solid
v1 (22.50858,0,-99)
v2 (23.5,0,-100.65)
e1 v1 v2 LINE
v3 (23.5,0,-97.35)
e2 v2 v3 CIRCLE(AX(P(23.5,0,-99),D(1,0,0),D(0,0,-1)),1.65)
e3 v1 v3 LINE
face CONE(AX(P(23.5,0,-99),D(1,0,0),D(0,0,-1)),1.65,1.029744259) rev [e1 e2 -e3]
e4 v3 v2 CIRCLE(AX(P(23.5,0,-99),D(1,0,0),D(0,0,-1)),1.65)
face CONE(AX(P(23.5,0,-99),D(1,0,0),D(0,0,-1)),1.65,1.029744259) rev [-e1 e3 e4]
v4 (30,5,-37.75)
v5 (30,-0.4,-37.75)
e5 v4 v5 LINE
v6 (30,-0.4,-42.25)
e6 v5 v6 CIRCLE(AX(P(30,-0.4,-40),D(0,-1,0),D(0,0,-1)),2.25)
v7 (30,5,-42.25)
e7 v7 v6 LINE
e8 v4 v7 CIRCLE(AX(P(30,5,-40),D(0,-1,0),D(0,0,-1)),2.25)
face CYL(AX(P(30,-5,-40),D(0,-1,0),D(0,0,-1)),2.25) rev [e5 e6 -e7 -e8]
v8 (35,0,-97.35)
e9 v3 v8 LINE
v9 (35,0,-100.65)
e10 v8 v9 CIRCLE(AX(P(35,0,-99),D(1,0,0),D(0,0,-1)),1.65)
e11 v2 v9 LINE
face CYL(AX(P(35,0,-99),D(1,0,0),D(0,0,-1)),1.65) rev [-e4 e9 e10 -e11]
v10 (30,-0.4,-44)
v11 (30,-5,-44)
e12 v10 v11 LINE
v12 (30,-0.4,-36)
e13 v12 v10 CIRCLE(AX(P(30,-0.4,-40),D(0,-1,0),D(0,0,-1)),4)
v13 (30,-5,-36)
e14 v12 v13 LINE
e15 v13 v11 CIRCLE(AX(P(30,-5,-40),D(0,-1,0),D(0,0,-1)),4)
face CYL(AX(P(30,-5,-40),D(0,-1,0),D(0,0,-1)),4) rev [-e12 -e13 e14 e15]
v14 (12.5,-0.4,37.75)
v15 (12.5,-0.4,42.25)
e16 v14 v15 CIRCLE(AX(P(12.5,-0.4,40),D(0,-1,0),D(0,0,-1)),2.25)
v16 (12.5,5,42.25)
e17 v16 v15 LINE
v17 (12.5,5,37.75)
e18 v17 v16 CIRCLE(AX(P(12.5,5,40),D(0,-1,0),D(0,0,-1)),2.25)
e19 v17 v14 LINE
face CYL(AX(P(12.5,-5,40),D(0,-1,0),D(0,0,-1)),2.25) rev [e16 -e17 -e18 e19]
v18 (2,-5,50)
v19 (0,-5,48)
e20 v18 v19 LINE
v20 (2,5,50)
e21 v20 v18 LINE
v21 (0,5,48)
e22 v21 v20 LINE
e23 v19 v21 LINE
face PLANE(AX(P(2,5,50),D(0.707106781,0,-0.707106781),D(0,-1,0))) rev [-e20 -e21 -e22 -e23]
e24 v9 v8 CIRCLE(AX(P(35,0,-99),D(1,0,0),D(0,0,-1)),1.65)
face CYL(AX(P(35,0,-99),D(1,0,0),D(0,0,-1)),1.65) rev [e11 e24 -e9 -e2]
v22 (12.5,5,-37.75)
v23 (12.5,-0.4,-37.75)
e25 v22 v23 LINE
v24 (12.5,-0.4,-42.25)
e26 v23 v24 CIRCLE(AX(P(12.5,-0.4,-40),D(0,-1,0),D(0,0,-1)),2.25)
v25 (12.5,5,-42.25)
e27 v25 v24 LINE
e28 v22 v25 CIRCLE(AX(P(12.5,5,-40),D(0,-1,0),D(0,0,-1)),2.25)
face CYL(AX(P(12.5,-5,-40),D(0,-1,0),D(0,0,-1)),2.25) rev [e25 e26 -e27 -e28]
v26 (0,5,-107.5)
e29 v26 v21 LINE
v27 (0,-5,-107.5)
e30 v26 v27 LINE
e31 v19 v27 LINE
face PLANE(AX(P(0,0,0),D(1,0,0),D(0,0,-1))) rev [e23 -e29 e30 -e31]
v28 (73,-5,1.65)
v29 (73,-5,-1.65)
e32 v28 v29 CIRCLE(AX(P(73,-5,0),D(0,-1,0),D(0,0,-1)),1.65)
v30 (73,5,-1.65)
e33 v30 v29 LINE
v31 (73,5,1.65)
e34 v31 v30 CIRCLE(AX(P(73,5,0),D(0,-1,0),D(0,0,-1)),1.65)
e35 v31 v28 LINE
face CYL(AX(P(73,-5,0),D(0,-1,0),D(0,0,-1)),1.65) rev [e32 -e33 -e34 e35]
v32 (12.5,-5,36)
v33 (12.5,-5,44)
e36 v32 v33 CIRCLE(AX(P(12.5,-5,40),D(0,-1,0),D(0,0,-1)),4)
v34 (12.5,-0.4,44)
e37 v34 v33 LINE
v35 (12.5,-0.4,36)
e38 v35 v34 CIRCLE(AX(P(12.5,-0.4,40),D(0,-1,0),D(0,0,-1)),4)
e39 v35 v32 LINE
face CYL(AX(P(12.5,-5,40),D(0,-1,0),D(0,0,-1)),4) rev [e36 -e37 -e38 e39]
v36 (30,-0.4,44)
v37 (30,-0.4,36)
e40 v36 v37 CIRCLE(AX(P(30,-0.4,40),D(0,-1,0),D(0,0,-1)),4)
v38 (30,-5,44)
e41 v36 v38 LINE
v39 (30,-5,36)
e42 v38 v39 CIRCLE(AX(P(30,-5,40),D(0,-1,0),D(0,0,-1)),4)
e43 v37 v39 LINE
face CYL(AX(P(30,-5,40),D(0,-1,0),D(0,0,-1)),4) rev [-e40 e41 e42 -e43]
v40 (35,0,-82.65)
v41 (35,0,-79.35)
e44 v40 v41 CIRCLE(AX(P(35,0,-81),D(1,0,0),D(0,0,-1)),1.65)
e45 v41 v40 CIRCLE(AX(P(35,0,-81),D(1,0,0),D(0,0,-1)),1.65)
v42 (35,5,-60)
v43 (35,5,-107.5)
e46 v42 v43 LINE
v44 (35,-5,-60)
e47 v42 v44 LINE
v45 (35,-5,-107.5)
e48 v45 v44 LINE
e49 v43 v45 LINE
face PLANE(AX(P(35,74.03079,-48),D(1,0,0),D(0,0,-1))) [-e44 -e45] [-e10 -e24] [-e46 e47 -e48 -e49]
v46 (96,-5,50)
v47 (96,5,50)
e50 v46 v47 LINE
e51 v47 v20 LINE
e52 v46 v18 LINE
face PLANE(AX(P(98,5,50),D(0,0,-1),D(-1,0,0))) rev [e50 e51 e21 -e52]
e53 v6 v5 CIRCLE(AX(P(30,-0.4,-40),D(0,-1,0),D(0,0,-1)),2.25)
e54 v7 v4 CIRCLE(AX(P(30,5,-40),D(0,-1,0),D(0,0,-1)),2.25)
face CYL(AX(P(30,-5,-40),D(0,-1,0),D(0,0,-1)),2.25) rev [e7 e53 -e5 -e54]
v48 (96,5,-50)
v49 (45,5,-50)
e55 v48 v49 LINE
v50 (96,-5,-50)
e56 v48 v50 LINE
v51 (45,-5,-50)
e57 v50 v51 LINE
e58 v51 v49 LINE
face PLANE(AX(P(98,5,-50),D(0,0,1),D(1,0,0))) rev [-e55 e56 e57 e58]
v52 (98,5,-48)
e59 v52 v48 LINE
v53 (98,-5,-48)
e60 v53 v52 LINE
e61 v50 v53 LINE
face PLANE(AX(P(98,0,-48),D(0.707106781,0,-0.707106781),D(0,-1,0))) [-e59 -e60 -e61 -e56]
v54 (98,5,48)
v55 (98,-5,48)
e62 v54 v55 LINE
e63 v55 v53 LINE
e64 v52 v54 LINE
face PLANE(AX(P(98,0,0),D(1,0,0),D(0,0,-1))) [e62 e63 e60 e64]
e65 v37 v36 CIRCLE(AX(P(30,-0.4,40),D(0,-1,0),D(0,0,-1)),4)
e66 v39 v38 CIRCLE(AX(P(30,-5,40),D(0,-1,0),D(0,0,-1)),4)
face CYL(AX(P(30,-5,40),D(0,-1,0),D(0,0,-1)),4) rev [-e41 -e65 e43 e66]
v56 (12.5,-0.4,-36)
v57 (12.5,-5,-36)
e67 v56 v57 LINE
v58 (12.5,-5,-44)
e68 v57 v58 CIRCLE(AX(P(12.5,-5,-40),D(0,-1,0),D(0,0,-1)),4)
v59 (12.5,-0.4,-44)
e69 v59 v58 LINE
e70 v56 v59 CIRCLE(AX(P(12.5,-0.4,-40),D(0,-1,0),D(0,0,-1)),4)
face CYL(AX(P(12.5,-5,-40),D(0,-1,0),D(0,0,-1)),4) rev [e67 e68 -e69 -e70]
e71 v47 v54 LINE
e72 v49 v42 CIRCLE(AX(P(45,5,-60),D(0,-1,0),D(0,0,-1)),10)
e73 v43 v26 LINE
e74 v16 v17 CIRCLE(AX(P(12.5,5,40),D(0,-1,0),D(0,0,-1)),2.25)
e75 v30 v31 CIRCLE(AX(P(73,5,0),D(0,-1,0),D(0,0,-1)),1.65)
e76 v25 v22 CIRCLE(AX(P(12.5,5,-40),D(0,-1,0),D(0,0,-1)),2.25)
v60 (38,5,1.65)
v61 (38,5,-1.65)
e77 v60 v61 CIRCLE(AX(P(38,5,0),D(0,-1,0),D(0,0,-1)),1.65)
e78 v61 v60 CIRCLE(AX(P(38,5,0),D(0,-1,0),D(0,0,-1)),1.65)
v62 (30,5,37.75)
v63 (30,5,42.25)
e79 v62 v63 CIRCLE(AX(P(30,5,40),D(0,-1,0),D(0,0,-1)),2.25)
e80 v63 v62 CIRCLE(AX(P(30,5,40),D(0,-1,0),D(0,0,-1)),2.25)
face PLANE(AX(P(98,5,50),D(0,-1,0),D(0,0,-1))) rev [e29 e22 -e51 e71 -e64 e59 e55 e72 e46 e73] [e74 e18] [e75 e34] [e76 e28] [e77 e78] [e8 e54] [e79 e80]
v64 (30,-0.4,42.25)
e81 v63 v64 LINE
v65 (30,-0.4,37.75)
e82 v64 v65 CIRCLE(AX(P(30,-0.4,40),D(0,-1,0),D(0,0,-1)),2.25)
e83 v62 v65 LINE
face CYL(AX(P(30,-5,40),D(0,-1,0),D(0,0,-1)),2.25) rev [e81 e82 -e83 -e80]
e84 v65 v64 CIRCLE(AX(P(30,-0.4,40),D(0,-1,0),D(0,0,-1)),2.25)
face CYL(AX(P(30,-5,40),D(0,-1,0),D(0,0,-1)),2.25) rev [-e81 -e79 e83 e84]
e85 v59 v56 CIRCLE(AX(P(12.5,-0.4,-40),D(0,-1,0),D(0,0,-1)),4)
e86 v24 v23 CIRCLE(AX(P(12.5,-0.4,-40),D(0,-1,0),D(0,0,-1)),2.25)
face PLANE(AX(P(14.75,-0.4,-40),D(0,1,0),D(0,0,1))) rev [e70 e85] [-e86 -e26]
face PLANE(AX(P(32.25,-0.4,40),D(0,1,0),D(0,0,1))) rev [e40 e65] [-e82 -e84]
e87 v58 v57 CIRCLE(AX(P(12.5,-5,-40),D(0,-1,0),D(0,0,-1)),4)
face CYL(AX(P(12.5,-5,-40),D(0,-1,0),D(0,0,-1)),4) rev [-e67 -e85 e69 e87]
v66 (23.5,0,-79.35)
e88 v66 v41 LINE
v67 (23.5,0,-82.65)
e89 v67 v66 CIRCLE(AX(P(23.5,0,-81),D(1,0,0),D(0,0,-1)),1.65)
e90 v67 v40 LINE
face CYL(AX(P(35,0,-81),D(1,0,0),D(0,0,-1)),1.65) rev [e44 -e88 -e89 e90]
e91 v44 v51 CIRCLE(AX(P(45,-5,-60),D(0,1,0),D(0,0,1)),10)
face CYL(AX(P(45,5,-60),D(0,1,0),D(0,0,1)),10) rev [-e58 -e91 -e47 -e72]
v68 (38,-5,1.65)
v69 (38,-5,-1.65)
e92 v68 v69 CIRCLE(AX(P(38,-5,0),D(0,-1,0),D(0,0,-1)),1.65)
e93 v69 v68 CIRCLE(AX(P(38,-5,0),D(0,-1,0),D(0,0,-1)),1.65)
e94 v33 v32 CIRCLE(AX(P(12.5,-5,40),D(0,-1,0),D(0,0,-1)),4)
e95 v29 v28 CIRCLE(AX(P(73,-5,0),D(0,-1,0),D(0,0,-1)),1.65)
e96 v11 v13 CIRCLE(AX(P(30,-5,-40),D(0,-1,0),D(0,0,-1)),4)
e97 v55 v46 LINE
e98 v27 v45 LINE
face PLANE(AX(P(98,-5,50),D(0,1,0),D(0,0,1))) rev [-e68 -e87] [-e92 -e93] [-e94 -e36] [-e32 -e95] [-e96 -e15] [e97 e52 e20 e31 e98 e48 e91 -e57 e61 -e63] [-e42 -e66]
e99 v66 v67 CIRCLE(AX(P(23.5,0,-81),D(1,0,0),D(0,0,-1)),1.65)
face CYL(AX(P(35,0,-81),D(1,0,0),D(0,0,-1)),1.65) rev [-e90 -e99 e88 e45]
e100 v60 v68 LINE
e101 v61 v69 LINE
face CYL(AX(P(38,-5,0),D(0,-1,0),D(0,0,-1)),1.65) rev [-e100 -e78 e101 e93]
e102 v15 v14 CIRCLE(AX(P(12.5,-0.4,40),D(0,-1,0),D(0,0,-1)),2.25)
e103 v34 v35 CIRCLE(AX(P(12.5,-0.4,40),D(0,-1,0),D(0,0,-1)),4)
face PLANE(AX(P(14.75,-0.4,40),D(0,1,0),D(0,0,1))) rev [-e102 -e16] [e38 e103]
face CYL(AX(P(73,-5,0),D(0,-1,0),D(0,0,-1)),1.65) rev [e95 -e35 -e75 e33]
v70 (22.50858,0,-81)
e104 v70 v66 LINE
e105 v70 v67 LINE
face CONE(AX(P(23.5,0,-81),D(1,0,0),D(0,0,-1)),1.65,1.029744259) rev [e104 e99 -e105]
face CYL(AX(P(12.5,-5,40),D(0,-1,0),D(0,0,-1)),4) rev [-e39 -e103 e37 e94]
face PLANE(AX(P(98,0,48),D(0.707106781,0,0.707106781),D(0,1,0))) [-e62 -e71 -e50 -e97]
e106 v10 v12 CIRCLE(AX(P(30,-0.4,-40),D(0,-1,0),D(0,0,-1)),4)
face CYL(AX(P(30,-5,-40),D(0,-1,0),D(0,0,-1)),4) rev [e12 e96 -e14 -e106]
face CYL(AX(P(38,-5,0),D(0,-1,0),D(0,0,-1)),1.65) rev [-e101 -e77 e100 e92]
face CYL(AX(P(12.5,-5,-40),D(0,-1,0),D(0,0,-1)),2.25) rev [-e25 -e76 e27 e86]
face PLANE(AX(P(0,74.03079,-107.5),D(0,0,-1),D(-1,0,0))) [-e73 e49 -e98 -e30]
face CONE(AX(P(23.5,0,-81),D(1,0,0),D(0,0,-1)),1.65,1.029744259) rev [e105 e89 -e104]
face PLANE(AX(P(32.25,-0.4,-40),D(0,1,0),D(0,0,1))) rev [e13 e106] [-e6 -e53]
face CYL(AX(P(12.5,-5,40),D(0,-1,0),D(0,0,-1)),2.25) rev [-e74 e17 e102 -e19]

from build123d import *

# Parameters (mm, degrees)
SKETCH_2_W                = 100
SKETCH_2_H                = 10
EXTRUDE_1_DEPTH           = 98
HOLE_WIZARD_1_D           = 4.5
HOLE_WIZARD_1_CBORE_D     = 8
HOLE_WIZARD_1_CBORE_DEPTH = 4.6
CHAMFER_1_SIZE            = 2
HOLE_WIZARD_M4_1_D        = 3.3
SKETCH_9_W                = 35
SKETCH_9_H                = 59.5
EXTRUDE_2_DEPTH           = 10
FILLET_1_R                = 10
HOLE_WIZARD_M4_2_D        = 3.3
HOLE_WIZARD_M4_2_DEPTH    = 11.5
HOLE_WIZARD_M4_2_TIP      = 0.991420021


with BuildPart() as part:
    # 草图2 → 凸台-拉伸1 (new body)
    with BuildSketch(Plane(origin=(0, 0, 0), x_dir=(0, 0, -1), z_dir=(1, 0, 0))):
        Rectangle(SKETCH_2_W, SKETCH_2_H)
    extrude(amount=EXTRUDE_1_DEPTH)

    # 打孔尺寸(%根据)开槽圆柱头螺钉的类型1 (through all)
    with Locations(Plane(origin=(0, -5, 0), x_dir=(-1, 0, 0), z_dir=(0, -1, 0))):
        with Locations((-30, 40), (-30, -40), (-12.5, -40), (-12.5, 40)):
            CounterBoreHole(HOLE_WIZARD_1_D / 2, HOLE_WIZARD_1_CBORE_D / 2, HOLE_WIZARD_1_CBORE_DEPTH)

    # 倒角1
    chamfer_1_edges = [part.edges().sort_by_distance(p)[0] for p in [
        (98, 0, 50),
        (98, 0, -50),
        (0, 0, 50),
        (0, 0, -50),
    ]]
    chamfer(chamfer_1_edges, length=CHAMFER_1_SIZE)

    # M4 螺纹孔1 (through all)
    with Locations(Plane(origin=(0, -5, 0), x_dir=(-1, 0, 0), z_dir=(0, -1, 0))):
        with Locations((-73, 0), (-38, 0)):
            Hole(HOLE_WIZARD_M4_1_D / 2)

    # 草图9 → 凸台-拉伸2 (add)
    with BuildSketch(Plane.XZ.offset(5)):
        with Locations((17.5, -77.75)):
            Rectangle(SKETCH_9_W, SKETCH_9_H)
    extrude(amount=-EXTRUDE_2_DEPTH)

    # 圆角1
    fillet_1_edges = [part.edges().sort_by_distance(p)[0] for p in [
        (35, 0, -50),
    ]]
    fillet(fillet_1_edges, radius=FILLET_1_R)

    # M4 螺纹孔2
    with Locations(Plane(origin=(35, 0, 0), x_dir=(0, 0, -1), z_dir=(1, 0, 0))):
        with Locations((99, 0), (81, 0)):
            Hole(HOLE_WIZARD_M4_2_D / 2, depth=HOLE_WIZARD_M4_2_DEPTH)
            with Locations((0, 0, -(HOLE_WIZARD_M4_2_DEPTH + HOLE_WIZARD_M4_2_TIP / 2))):  # 118° drill point
                Cone(0, HOLE_WIZARD_M4_2_D / 2, HOLE_WIZARD_M4_2_TIP, mode=Mode.SUBTRACT)


solid = part.part
